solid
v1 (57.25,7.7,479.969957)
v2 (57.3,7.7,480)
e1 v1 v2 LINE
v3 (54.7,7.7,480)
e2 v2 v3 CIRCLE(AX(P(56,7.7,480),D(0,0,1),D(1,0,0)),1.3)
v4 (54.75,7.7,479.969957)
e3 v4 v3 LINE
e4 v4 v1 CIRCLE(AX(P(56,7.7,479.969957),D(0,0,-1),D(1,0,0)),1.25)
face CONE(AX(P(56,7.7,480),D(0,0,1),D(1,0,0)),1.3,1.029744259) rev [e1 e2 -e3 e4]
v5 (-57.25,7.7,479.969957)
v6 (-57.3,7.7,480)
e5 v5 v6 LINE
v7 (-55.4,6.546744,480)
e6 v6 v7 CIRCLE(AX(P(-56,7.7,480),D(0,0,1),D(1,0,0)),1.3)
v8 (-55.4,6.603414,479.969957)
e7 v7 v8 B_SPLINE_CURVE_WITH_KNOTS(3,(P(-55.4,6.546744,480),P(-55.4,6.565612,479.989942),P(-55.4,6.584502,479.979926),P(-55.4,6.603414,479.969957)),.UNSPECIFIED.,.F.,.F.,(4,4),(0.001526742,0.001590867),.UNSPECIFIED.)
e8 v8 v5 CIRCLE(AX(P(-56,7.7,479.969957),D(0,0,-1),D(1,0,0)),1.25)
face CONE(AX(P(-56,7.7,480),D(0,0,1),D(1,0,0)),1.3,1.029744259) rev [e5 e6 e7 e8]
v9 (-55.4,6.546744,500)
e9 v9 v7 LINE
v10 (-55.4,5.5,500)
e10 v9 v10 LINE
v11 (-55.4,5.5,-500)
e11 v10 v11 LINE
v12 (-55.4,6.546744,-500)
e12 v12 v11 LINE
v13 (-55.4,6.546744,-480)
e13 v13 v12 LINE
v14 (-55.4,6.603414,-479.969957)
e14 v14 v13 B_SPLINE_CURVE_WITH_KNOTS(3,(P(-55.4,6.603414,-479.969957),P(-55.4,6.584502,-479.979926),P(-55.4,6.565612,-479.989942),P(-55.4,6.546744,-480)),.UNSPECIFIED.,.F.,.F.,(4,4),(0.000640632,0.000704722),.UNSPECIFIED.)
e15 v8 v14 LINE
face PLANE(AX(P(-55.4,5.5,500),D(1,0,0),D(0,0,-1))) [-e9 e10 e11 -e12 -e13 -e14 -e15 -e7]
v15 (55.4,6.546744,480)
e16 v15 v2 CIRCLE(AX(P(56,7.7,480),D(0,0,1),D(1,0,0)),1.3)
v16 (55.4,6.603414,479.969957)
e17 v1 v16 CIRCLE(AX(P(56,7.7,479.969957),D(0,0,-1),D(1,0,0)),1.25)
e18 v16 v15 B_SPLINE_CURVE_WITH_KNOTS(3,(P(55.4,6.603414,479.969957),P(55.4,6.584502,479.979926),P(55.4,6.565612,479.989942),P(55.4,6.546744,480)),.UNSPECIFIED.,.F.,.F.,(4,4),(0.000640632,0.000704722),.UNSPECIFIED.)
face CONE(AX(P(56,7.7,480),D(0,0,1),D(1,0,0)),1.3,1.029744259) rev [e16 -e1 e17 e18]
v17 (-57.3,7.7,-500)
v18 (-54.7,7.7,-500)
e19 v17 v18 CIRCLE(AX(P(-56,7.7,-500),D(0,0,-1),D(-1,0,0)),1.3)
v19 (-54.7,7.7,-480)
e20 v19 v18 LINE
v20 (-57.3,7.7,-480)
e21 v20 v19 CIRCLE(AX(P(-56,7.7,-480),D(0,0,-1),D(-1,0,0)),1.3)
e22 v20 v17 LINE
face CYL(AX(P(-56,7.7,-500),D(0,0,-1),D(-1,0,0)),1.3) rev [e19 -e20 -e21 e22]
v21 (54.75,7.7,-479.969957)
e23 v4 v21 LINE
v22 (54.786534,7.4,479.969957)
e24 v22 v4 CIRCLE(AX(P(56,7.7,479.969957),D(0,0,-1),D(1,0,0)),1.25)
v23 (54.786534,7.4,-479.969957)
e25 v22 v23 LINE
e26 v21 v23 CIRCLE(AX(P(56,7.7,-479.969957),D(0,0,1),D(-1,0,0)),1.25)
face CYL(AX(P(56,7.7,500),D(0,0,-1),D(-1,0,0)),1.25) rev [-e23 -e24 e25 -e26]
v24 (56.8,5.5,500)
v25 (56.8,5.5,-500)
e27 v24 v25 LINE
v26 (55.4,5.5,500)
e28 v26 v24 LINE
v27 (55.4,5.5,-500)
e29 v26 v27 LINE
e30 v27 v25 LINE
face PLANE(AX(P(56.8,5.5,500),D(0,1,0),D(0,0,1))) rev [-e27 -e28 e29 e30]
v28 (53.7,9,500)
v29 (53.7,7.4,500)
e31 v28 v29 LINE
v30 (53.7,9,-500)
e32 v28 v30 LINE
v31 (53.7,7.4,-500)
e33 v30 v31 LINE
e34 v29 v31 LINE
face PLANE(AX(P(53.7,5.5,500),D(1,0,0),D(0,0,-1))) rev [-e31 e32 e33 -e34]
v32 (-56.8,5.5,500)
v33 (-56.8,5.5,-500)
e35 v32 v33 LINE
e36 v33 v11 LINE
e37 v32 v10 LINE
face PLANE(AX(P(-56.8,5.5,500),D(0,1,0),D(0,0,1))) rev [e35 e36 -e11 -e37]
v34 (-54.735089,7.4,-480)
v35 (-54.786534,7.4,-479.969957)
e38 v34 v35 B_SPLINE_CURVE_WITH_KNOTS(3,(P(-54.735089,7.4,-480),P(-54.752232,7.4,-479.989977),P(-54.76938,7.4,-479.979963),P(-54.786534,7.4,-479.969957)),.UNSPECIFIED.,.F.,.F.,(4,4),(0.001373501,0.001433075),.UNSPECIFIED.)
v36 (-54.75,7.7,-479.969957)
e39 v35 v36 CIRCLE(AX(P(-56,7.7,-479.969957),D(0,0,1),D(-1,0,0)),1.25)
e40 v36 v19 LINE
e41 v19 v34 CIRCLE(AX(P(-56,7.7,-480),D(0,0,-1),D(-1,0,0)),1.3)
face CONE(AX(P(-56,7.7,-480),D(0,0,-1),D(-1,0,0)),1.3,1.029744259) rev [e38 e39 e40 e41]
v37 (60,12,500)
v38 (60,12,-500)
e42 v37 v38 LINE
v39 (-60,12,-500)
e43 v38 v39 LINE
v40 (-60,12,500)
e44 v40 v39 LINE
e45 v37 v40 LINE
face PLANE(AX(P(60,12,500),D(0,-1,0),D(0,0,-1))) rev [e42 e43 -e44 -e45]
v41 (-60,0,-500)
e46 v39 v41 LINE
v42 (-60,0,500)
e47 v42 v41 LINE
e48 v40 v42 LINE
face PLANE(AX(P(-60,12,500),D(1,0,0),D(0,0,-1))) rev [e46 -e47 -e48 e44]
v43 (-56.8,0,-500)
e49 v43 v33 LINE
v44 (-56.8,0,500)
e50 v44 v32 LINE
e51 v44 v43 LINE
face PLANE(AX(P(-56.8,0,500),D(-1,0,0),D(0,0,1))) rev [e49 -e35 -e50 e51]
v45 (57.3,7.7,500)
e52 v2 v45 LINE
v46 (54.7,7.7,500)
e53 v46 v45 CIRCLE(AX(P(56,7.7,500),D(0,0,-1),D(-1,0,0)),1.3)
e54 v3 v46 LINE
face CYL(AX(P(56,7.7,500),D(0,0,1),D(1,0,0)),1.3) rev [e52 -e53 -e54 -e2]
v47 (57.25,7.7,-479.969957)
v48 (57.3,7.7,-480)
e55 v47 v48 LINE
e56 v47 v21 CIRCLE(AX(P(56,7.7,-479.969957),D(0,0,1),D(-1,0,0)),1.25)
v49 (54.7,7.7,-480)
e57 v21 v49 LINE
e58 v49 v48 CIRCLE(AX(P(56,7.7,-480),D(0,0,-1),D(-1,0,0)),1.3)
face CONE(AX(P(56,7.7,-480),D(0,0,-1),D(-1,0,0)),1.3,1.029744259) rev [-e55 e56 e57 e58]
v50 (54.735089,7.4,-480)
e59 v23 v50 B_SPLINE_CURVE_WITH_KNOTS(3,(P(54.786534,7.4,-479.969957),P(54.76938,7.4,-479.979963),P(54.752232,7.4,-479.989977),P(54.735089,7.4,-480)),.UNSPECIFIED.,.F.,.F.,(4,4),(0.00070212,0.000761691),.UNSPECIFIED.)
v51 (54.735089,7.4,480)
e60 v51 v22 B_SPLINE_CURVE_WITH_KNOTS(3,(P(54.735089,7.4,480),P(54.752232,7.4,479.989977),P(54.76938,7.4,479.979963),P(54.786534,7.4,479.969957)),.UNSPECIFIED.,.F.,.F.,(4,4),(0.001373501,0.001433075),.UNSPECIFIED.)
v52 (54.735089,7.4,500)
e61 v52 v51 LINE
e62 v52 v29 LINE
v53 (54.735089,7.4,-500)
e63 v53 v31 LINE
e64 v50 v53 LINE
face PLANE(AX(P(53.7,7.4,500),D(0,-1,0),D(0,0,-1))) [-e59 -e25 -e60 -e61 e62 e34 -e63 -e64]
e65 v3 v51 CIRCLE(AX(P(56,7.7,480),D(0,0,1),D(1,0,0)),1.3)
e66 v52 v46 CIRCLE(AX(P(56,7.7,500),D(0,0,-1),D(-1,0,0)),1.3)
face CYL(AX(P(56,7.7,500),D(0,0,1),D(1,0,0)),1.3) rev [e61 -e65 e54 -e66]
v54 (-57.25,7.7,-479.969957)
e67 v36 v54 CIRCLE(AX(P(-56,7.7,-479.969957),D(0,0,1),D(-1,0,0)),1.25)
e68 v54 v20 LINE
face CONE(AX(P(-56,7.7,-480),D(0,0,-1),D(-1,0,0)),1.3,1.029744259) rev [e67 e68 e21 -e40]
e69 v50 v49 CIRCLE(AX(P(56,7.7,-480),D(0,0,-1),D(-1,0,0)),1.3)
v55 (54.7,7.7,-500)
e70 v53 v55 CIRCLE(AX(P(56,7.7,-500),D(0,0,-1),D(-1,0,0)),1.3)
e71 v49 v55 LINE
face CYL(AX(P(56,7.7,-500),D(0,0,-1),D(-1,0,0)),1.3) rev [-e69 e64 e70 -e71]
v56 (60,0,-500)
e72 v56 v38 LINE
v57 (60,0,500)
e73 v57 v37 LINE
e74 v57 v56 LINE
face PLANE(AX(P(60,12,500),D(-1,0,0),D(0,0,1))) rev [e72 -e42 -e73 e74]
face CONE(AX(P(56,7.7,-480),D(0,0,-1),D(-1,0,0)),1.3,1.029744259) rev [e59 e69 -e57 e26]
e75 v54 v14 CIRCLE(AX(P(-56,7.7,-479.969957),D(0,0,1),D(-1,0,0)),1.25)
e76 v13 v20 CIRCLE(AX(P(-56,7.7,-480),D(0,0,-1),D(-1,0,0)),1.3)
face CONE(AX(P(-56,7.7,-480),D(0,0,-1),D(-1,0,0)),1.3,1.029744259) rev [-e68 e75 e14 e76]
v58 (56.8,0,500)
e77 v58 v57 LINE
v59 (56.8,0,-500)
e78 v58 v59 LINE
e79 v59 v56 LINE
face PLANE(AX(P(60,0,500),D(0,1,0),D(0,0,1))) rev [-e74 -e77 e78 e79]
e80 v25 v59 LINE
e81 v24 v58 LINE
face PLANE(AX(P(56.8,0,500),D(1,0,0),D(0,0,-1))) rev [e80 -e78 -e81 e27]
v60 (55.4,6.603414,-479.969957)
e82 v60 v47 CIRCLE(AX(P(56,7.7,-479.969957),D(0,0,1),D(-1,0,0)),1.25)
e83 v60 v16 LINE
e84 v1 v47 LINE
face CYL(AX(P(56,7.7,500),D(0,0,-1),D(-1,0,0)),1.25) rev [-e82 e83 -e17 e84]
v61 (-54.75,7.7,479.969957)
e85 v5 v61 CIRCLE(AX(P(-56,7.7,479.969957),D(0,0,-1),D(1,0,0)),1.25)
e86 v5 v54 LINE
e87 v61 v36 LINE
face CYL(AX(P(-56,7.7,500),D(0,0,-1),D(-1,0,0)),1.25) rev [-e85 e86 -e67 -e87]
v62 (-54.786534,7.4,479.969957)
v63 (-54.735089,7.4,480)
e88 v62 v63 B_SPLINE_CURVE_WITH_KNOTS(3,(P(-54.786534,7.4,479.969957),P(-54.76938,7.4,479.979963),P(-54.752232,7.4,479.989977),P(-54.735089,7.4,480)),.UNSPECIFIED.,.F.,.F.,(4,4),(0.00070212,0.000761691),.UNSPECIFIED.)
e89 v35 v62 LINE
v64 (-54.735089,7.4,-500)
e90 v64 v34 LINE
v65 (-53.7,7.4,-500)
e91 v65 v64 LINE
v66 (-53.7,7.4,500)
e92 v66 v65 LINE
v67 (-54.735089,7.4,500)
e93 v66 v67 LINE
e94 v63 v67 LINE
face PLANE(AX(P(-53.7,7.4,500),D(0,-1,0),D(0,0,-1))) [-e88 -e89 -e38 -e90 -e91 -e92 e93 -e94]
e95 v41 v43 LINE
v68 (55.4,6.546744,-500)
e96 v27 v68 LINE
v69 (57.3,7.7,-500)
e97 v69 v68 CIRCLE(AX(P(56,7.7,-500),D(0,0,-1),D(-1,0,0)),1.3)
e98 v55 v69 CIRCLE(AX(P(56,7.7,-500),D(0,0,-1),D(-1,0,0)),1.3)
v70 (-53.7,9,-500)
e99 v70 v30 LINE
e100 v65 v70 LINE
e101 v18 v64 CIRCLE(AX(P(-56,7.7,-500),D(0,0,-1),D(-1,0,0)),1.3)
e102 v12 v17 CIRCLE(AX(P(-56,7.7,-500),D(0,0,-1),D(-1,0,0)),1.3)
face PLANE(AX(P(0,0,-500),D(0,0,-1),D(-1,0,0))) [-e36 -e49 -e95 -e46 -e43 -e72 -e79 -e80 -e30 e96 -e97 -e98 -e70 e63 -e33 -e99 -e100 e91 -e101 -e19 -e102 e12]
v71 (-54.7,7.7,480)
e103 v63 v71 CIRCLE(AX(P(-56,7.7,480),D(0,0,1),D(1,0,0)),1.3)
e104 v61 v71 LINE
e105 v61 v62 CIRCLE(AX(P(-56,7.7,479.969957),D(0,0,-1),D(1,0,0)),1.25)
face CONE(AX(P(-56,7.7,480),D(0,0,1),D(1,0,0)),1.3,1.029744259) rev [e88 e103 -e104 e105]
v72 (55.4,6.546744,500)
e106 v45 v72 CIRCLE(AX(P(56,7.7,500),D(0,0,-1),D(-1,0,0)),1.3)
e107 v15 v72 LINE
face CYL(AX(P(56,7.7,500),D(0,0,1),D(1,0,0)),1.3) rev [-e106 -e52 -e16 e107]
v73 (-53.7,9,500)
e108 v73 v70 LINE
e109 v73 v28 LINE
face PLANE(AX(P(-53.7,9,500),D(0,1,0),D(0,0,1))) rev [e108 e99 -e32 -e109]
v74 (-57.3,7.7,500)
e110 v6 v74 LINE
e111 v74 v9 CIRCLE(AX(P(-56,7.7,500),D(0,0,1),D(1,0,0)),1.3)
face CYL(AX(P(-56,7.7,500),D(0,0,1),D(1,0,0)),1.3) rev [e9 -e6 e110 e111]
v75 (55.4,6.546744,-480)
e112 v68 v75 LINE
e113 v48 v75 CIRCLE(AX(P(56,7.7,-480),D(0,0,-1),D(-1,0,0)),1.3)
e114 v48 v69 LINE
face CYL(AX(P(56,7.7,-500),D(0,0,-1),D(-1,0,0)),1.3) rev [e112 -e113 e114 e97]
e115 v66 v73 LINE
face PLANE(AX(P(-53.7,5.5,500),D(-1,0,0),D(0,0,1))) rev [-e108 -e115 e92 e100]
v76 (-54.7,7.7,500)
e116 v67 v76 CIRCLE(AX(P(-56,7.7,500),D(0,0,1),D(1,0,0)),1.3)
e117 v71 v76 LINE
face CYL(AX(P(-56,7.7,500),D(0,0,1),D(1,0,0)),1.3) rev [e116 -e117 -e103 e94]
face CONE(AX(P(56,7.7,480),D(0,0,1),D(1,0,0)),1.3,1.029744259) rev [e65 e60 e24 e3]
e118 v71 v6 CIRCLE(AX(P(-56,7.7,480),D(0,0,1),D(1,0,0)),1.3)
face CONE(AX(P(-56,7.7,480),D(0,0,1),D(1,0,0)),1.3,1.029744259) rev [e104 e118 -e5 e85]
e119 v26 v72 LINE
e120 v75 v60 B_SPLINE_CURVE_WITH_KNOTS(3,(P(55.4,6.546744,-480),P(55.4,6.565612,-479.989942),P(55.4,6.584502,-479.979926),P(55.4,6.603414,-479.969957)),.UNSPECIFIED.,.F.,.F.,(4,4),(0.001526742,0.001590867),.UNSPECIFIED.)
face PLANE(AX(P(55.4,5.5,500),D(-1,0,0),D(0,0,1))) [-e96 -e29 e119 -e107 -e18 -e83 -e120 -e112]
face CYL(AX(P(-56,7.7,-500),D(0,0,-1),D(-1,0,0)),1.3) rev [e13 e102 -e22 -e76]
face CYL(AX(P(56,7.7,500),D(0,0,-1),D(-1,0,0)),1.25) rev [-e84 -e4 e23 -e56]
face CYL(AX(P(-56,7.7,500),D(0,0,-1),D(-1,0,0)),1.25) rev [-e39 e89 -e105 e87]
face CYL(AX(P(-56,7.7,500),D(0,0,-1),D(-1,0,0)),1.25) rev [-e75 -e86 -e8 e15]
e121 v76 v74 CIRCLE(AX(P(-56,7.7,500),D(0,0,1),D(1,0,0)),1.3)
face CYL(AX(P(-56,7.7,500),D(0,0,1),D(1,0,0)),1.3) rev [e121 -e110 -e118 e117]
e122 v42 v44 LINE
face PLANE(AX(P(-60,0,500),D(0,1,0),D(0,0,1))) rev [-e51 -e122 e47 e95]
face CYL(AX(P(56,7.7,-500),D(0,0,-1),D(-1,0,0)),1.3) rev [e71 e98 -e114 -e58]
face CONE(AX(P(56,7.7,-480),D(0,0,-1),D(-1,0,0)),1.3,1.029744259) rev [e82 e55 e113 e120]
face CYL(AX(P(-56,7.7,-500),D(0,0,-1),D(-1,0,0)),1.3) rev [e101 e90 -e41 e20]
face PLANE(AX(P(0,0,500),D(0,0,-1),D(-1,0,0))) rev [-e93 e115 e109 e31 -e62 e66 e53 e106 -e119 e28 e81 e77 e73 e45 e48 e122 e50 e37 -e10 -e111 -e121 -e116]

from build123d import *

# Parameters (mm, degrees)
SKETCH_1_R                  = 1.25
EXTRUDE_1_DEPTH             = 500
CUT_EXTRUDE_1_DEPTH         = 504.730086455
CUT_EXTRUDE_1_DEPTH_BACK    = 504.730086455
SKETCH_2_W                  = 1.7
SKETCH_2_H                  = 1.9
HOLE_WIZARD_M3_1_AT_2_COUNT = 2
HOLE_WIZARD_M3_1_AT_2_PITCH = 112


with BuildPart() as part:
    # 草图1 → 凸台-拉伸1 (new, symmetric)
    with BuildSketch(Plane.XY):
        Polygon((60, 12), (-60, 12), (-60, 0), (-56.8, 0), (-56.8, 5.5), (-53.7, 5.5), (-53.7, 9), (53.7, 9), (53.7, 5.5), (56.8, 5.5), (56.8, 0), (60, 0), align=None)
        with Locations((-56, 7.7)):
            Circle(SKETCH_1_R, mode=Mode.SUBTRACT)
        with Locations(Location((56, 7.7, 0), (0, 0, 180))):
            Circle(SKETCH_1_R, mode=Mode.SUBTRACT)
    extrude(amount=EXTRUDE_1_DEPTH, both=True)

    # 草图2 → 切除-拉伸1 (cut, two sides: drawn at the far end of the back side and taken through both)
    with BuildSketch(Plane.XY.offset(-CUT_EXTRUDE_1_DEPTH_BACK)):
        with Locations((-54.55, 6.45)):
            Rectangle(SKETCH_2_W, SKETCH_2_H)
        with Locations((54.55, 6.45)):
            Rectangle(SKETCH_2_W, SKETCH_2_H)
    extrude(amount=CUT_EXTRUDE_1_DEPTH + CUT_EXTRUDE_1_DEPTH_BACK, mode=Mode.SUBTRACT)

    # 草图7 → M3 螺纹孔1 (revolve, cut)
    with BuildSketch(Plane(origin=(-56, 7.7, 500), x_dir=(0, -1, 0), z_dir=(1, 0, 0))):
        Polygon((0, 0), (0, 20.781118805), (1.3, 20), (1.3, 0), align=None)
    hole_wizard_m3_1 = revolve(axis=Axis((-56, 7.7, 506.35), (0, 0, -1)), mode=Mode.SUBTRACT)

    # M3 螺纹孔1 at 2: M3 螺纹孔1 ×2
    with Locations(*[(i * HOLE_WIZARD_M3_1_AT_2_PITCH, 0, 0) for i in range(1, HOLE_WIZARD_M3_1_AT_2_COUNT)]):
        add(hole_wizard_m3_1, mode=Mode.SUBTRACT)

    # 镜向1: M3 螺纹孔1 across plane
    add(hole_wizard_m3_1.mirror(Plane.XY), mode=Mode.SUBTRACT)

    # 镜向1 copy 1 sketch → 镜向1 copy 1 (revolve, cut)
    with BuildSketch(Plane(origin=(56, 7.7, -500), x_dir=(0, -1, 0), z_dir=(1, 0, 0))):
        Polygon((0, 0), (0, -20.781118805), (1.3, -20), (1.3, 0), align=None)
    revolve(axis=Axis((56, 7.7, -506.35), (0, 0, -1)), mode=Mode.SUBTRACT)


solid = part.part
